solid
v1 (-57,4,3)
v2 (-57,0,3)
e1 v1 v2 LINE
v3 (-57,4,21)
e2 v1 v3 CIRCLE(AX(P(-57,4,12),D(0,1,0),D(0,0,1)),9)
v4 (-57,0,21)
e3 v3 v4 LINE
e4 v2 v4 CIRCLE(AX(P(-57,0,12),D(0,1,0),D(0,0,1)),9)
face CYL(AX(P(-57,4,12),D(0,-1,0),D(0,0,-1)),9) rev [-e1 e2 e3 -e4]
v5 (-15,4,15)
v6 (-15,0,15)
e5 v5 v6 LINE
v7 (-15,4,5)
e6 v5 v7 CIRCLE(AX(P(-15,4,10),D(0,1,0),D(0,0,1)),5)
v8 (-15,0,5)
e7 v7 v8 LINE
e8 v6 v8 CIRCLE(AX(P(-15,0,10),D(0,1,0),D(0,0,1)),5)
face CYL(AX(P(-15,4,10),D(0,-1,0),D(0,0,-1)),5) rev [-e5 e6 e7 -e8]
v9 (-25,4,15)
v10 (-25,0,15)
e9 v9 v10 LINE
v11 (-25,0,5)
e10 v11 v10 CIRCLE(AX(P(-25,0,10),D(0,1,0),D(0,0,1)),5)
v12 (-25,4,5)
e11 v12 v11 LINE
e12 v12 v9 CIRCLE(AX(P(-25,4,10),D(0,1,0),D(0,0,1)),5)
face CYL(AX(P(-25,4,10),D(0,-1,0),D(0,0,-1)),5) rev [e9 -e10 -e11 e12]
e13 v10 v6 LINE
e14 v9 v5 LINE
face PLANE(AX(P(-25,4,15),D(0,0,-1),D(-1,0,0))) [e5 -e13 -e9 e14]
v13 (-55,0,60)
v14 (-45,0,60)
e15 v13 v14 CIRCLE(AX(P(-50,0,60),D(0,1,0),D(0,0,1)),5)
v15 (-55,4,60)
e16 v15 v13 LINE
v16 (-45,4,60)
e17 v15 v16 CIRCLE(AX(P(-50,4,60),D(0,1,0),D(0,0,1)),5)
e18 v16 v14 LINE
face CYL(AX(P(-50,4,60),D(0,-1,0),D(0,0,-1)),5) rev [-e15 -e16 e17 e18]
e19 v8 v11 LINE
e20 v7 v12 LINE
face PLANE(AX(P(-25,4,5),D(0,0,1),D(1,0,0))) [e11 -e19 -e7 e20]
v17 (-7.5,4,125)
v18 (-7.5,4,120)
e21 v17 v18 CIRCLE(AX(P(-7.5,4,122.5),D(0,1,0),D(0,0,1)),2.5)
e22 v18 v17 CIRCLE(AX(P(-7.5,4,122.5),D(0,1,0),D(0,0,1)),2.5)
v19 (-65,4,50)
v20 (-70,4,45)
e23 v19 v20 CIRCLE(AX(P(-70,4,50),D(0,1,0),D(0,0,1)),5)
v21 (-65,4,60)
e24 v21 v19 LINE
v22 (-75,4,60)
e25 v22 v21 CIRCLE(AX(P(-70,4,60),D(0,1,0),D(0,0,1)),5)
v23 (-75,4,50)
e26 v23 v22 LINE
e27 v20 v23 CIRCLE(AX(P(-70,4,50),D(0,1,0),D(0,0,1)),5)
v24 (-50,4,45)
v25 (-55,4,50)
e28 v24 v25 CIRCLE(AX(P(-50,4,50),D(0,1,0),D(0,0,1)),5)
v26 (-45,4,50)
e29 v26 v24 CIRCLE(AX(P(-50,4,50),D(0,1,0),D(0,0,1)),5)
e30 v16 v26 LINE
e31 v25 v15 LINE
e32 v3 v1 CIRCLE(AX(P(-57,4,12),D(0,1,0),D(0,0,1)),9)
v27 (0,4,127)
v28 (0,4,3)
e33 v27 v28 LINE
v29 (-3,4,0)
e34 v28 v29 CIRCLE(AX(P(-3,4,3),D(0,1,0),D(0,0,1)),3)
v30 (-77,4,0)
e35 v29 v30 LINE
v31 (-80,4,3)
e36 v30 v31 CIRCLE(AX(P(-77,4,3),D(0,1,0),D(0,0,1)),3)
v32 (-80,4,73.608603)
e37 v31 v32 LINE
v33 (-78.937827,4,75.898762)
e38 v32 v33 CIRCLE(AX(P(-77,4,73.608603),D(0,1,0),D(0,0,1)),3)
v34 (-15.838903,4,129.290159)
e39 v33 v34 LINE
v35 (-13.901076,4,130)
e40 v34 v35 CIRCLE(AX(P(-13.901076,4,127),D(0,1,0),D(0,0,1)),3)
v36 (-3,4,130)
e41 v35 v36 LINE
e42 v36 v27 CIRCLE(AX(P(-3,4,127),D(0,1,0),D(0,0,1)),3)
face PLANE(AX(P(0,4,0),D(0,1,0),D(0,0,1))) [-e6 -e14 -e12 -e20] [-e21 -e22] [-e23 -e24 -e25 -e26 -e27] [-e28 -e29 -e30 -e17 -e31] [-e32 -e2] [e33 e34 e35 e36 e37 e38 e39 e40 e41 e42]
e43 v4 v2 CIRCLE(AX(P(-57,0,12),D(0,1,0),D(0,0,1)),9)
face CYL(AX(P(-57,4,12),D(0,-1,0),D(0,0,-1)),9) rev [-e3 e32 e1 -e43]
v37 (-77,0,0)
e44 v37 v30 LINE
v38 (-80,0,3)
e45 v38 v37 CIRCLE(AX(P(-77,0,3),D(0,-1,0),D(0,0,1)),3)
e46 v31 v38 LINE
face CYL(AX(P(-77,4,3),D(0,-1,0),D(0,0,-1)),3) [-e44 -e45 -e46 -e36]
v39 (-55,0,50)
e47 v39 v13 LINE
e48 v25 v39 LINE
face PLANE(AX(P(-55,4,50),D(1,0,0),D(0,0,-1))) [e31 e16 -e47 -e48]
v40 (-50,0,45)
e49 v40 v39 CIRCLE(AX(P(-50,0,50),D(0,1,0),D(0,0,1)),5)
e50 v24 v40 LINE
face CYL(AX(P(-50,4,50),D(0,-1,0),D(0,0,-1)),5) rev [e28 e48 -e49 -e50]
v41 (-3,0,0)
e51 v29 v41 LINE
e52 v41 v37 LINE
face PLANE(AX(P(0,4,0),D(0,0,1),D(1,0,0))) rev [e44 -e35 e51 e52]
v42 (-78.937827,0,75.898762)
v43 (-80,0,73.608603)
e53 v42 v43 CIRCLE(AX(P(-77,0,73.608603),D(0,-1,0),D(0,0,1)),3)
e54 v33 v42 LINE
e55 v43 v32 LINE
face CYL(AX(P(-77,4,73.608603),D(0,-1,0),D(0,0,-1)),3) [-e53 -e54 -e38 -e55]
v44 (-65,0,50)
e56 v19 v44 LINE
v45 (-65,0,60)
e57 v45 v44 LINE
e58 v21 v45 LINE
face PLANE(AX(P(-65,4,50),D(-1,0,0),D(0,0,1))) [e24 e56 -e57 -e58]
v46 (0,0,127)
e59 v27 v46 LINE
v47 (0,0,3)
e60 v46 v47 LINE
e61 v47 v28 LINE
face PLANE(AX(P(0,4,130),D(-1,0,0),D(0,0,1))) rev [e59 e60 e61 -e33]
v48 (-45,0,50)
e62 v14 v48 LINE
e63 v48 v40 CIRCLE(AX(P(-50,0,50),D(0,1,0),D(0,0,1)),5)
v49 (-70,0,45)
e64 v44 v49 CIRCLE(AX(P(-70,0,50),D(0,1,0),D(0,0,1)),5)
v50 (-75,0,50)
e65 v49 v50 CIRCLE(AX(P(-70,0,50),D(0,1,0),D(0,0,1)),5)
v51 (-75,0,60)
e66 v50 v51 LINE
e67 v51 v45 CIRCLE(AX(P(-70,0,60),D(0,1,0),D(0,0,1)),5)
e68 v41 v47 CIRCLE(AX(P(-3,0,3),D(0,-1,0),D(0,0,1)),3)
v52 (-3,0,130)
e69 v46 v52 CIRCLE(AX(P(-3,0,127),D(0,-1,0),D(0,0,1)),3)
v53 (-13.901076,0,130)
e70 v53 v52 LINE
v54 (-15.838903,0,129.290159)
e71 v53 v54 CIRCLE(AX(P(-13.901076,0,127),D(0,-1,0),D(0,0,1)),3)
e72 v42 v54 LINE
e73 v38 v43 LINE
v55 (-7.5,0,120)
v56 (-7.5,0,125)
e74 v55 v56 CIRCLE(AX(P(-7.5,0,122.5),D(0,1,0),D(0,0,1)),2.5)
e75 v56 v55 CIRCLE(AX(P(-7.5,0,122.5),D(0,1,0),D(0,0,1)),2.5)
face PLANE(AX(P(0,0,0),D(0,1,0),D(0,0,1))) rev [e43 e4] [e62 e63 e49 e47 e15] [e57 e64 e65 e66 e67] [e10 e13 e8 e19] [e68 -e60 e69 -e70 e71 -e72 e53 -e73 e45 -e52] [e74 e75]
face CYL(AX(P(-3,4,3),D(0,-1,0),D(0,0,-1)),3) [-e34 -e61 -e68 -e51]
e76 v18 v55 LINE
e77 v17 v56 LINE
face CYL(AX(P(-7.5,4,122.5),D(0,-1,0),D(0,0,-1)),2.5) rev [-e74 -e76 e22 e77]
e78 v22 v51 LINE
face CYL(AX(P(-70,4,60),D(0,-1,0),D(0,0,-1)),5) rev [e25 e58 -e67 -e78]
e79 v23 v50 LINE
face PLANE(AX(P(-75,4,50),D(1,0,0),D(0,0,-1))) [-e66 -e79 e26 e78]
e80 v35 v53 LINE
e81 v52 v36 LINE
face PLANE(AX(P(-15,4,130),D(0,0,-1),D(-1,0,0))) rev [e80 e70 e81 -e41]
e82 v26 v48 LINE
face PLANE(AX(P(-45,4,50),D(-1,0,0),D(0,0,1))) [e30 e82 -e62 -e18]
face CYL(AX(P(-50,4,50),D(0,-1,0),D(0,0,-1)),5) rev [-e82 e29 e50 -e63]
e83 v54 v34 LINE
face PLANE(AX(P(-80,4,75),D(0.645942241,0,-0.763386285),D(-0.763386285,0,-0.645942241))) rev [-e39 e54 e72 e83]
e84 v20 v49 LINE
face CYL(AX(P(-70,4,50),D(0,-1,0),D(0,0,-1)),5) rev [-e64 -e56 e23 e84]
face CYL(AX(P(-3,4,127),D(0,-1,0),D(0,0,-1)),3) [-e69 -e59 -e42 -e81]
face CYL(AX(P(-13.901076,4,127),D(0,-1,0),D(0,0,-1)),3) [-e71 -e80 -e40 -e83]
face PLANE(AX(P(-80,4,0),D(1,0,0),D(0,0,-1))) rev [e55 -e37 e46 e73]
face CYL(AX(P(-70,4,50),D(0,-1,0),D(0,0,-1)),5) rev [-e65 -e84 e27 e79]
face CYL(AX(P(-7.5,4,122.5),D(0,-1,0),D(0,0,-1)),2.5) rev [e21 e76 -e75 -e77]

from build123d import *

# Parameters (mm, degrees)
SKETCH1_R           = 9
SKETCH1_R_2         = 2.5
BOSS_EXTRUDE1_DEPTH = 4
FILLET1_R           = 3


with BuildPart() as part:
    # Sketch1 → Boss-Extrude1 (new body)
    with BuildSketch(Plane(origin=(0, 0, 0), x_dir=(1, 0, 0), z_dir=(0, 1, 0))):
        Polygon((0, 0), (-80, 0), (-80, -75), (-15, -130), (0, -130), align=None)
        with Locations(Location((-57, -12, 0), (0, 0, 270))):
            Circle(SKETCH1_R, mode=Mode.SUBTRACT)
        with Locations(Location((-7.5, -122.5, 0), (0, 0, 270))):
            Circle(SKETCH1_R_2, mode=Mode.SUBTRACT)
        with BuildLine():
            Line((-25, -5), (-15, -5))
            ThreePointArc((-15, -5), (-10, -10), (-15, -15))
            Line((-15, -15), (-25, -15))
            ThreePointArc((-25, -15), (-30, -10), (-25, -5))
        make_face(mode=Mode.SUBTRACT)
        with BuildLine():
            Line((-65, -50), (-65, -60))
            ThreePointArc((-65, -60), (-70, -65), (-75, -60))
            Line((-75, -60), (-75, -50))
            ThreePointArc((-75, -50), (-70, -45), (-65, -50))
        make_face(mode=Mode.SUBTRACT)
        with BuildLine():
            Line((-45, -50), (-45, -60))
            ThreePointArc((-45, -60), (-50, -65), (-55, -60))
            Line((-55, -60), (-55, -50))
            ThreePointArc((-55, -50), (-50, -45), (-45, -50))
        make_face(mode=Mode.SUBTRACT)
    extrude(amount=BOSS_EXTRUDE1_DEPTH)

    # Fillet1
    fillet1_edges = [part.edges().sort_by_distance(p)[0] for p in [
        (0, 2, 130),
        (-15, 2, 130),
        (-80, 2, 75),
        (-80, 2, 0),
        (0, 2, 0),
    ]]
    fillet(fillet1_edges, radius=FILLET1_R)


solid = part.part
